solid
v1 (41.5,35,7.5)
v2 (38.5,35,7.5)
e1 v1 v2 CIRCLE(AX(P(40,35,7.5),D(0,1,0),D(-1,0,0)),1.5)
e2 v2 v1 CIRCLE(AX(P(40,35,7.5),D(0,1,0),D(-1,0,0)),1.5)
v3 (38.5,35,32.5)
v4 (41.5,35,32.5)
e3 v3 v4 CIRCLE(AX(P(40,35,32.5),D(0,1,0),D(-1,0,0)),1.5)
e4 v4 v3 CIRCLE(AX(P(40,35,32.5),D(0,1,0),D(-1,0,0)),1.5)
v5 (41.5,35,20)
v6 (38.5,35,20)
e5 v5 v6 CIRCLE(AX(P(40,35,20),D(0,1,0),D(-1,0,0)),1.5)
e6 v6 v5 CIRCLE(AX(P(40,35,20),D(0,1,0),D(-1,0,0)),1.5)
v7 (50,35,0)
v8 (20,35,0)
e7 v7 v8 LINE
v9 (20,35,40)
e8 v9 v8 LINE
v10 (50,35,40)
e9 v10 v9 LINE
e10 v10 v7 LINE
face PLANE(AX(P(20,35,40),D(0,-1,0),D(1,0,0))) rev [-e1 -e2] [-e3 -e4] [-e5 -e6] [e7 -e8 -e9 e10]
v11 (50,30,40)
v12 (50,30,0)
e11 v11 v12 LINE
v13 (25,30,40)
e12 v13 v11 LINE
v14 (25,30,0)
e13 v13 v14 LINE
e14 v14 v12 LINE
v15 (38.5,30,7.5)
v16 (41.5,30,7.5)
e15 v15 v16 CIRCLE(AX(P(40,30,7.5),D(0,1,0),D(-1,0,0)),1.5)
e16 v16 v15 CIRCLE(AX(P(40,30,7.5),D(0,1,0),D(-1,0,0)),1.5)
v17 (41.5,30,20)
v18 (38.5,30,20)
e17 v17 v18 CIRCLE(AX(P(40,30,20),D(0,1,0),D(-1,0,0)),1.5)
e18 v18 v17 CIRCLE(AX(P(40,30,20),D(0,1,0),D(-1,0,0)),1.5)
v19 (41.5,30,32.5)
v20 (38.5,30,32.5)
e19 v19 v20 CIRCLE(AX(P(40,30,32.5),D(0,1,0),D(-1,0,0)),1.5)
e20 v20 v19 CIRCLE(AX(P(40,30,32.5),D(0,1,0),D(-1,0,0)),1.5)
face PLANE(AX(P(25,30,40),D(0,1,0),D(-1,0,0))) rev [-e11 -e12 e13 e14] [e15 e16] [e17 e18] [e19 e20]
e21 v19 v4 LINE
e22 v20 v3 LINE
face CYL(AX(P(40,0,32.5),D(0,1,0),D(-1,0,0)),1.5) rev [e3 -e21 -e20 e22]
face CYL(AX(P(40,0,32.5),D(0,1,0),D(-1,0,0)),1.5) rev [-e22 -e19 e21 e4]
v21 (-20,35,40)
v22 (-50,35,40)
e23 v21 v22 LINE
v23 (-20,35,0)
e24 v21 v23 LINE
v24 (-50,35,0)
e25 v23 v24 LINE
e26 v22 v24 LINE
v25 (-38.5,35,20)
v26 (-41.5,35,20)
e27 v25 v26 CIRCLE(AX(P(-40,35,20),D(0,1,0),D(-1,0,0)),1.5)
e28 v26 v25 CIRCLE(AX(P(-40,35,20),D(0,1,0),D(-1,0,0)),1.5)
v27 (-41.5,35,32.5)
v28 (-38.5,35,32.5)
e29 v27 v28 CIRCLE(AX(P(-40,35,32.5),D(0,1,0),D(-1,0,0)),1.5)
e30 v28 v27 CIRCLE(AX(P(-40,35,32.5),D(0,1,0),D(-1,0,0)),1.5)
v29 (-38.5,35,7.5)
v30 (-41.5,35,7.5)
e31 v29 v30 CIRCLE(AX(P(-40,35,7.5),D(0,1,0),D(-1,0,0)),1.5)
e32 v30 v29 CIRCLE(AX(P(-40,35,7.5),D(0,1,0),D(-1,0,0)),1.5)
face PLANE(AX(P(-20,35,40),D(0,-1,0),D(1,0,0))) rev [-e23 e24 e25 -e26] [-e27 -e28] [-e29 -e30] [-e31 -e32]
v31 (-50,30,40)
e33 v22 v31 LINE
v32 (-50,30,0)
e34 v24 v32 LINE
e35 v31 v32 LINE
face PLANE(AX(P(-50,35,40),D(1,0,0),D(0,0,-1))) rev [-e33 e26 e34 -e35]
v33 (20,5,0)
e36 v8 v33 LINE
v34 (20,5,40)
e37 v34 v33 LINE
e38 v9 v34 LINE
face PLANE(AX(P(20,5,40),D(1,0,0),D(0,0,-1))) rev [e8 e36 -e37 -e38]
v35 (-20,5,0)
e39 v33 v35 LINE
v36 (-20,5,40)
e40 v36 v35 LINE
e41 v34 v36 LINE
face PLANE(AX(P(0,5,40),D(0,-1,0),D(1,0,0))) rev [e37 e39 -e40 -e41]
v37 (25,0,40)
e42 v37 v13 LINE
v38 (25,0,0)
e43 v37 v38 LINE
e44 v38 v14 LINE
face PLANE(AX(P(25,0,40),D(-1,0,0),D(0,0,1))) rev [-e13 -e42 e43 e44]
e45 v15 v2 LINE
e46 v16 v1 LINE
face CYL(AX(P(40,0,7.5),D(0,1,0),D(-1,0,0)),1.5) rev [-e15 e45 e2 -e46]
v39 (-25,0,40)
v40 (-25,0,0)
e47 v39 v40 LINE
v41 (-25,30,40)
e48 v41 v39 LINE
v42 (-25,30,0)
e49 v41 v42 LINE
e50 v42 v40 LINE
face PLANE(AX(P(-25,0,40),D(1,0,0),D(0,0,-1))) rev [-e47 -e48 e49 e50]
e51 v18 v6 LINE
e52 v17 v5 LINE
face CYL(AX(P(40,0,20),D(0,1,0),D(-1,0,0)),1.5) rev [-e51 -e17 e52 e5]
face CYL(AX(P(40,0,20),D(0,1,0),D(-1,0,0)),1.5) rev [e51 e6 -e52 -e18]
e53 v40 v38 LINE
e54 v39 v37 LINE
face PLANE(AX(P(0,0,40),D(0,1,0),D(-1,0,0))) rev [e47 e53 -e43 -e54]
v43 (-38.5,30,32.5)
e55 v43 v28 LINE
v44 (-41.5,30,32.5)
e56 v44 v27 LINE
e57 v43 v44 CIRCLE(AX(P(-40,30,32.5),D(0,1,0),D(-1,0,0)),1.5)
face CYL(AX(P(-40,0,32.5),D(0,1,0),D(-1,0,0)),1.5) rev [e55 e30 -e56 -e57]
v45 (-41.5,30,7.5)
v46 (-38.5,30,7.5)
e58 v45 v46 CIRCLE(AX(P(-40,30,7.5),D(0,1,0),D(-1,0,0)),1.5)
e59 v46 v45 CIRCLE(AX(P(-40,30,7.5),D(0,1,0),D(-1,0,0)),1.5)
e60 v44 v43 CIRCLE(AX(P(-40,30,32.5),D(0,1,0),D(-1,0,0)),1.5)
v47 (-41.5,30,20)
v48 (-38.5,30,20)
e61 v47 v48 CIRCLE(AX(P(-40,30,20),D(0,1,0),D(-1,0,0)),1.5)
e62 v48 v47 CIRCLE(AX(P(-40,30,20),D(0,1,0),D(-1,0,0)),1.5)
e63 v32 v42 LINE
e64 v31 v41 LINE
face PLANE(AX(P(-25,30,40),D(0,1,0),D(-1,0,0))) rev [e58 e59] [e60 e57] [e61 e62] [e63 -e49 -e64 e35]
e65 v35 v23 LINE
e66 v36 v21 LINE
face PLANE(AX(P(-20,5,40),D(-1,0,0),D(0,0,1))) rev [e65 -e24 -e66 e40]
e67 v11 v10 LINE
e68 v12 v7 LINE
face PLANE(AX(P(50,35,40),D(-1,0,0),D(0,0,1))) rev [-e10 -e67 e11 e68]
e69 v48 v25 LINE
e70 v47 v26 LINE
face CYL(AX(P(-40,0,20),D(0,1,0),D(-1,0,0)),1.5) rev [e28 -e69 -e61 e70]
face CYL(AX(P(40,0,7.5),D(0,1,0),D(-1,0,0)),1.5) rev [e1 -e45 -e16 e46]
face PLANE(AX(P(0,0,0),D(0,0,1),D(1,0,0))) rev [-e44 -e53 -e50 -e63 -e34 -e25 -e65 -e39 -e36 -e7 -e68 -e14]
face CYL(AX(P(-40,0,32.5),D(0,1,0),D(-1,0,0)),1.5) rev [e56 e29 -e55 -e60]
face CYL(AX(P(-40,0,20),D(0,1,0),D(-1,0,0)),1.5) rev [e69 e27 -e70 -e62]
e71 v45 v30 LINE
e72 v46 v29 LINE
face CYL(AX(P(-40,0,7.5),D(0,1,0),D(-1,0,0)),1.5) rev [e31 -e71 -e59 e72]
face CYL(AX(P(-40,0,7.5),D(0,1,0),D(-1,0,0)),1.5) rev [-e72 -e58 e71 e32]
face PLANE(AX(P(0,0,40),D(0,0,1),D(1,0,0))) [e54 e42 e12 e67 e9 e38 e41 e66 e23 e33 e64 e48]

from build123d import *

# Parameters (mm, degrees)
BOSS_EXTRUDE1_DEPTH = 40
SKETCH2_R           = 1.5
CUT_EXTRUDE1_DEPTH  = 73.972597597


with BuildPart() as part:
    # Sketch1 → Boss-Extrude1 (new body)
    with BuildSketch(Plane.XY):
        Polygon((0, 0), (-25, 0), (-25, 30), (-50, 30), (-50, 35), (-20, 35), (-20, 5), (0, 5), (20, 5), (20, 35), (50, 35), (50, 30), (25, 30), (25, 0), align=None)
    extrude(amount=BOSS_EXTRUDE1_DEPTH)

    # Sketch2 → Cut-Extrude1 (cut, through all)
    with BuildSketch(Plane(origin=(0, 35, 0), x_dir=(1, 0, 0), z_dir=(0, 1, 0))):
        with Locations(Location((-40, -7.5, 0), (0, 0, 180))):
            Circle(SKETCH2_R)
        with Locations(Location((-40, -20, 0), (0, 0, 180))):
            Circle(SKETCH2_R)
        with Locations(Location((-40, -32.5, 0), (0, 0, 180))):
            Circle(SKETCH2_R)
        with Locations(Location((40, -7.5, 0), (0, 0, 180))):
            Circle(SKETCH2_R)
        with Locations(Location((40, -20, 0), (0, 0, 180))):
            Circle(SKETCH2_R)
        with Locations(Location((40, -32.5, 0), (0, 0, 180))):
            Circle(SKETCH2_R)
    extrude(amount=-CUT_EXTRUDE1_DEPTH, mode=Mode.SUBTRACT)


solid = part.part
